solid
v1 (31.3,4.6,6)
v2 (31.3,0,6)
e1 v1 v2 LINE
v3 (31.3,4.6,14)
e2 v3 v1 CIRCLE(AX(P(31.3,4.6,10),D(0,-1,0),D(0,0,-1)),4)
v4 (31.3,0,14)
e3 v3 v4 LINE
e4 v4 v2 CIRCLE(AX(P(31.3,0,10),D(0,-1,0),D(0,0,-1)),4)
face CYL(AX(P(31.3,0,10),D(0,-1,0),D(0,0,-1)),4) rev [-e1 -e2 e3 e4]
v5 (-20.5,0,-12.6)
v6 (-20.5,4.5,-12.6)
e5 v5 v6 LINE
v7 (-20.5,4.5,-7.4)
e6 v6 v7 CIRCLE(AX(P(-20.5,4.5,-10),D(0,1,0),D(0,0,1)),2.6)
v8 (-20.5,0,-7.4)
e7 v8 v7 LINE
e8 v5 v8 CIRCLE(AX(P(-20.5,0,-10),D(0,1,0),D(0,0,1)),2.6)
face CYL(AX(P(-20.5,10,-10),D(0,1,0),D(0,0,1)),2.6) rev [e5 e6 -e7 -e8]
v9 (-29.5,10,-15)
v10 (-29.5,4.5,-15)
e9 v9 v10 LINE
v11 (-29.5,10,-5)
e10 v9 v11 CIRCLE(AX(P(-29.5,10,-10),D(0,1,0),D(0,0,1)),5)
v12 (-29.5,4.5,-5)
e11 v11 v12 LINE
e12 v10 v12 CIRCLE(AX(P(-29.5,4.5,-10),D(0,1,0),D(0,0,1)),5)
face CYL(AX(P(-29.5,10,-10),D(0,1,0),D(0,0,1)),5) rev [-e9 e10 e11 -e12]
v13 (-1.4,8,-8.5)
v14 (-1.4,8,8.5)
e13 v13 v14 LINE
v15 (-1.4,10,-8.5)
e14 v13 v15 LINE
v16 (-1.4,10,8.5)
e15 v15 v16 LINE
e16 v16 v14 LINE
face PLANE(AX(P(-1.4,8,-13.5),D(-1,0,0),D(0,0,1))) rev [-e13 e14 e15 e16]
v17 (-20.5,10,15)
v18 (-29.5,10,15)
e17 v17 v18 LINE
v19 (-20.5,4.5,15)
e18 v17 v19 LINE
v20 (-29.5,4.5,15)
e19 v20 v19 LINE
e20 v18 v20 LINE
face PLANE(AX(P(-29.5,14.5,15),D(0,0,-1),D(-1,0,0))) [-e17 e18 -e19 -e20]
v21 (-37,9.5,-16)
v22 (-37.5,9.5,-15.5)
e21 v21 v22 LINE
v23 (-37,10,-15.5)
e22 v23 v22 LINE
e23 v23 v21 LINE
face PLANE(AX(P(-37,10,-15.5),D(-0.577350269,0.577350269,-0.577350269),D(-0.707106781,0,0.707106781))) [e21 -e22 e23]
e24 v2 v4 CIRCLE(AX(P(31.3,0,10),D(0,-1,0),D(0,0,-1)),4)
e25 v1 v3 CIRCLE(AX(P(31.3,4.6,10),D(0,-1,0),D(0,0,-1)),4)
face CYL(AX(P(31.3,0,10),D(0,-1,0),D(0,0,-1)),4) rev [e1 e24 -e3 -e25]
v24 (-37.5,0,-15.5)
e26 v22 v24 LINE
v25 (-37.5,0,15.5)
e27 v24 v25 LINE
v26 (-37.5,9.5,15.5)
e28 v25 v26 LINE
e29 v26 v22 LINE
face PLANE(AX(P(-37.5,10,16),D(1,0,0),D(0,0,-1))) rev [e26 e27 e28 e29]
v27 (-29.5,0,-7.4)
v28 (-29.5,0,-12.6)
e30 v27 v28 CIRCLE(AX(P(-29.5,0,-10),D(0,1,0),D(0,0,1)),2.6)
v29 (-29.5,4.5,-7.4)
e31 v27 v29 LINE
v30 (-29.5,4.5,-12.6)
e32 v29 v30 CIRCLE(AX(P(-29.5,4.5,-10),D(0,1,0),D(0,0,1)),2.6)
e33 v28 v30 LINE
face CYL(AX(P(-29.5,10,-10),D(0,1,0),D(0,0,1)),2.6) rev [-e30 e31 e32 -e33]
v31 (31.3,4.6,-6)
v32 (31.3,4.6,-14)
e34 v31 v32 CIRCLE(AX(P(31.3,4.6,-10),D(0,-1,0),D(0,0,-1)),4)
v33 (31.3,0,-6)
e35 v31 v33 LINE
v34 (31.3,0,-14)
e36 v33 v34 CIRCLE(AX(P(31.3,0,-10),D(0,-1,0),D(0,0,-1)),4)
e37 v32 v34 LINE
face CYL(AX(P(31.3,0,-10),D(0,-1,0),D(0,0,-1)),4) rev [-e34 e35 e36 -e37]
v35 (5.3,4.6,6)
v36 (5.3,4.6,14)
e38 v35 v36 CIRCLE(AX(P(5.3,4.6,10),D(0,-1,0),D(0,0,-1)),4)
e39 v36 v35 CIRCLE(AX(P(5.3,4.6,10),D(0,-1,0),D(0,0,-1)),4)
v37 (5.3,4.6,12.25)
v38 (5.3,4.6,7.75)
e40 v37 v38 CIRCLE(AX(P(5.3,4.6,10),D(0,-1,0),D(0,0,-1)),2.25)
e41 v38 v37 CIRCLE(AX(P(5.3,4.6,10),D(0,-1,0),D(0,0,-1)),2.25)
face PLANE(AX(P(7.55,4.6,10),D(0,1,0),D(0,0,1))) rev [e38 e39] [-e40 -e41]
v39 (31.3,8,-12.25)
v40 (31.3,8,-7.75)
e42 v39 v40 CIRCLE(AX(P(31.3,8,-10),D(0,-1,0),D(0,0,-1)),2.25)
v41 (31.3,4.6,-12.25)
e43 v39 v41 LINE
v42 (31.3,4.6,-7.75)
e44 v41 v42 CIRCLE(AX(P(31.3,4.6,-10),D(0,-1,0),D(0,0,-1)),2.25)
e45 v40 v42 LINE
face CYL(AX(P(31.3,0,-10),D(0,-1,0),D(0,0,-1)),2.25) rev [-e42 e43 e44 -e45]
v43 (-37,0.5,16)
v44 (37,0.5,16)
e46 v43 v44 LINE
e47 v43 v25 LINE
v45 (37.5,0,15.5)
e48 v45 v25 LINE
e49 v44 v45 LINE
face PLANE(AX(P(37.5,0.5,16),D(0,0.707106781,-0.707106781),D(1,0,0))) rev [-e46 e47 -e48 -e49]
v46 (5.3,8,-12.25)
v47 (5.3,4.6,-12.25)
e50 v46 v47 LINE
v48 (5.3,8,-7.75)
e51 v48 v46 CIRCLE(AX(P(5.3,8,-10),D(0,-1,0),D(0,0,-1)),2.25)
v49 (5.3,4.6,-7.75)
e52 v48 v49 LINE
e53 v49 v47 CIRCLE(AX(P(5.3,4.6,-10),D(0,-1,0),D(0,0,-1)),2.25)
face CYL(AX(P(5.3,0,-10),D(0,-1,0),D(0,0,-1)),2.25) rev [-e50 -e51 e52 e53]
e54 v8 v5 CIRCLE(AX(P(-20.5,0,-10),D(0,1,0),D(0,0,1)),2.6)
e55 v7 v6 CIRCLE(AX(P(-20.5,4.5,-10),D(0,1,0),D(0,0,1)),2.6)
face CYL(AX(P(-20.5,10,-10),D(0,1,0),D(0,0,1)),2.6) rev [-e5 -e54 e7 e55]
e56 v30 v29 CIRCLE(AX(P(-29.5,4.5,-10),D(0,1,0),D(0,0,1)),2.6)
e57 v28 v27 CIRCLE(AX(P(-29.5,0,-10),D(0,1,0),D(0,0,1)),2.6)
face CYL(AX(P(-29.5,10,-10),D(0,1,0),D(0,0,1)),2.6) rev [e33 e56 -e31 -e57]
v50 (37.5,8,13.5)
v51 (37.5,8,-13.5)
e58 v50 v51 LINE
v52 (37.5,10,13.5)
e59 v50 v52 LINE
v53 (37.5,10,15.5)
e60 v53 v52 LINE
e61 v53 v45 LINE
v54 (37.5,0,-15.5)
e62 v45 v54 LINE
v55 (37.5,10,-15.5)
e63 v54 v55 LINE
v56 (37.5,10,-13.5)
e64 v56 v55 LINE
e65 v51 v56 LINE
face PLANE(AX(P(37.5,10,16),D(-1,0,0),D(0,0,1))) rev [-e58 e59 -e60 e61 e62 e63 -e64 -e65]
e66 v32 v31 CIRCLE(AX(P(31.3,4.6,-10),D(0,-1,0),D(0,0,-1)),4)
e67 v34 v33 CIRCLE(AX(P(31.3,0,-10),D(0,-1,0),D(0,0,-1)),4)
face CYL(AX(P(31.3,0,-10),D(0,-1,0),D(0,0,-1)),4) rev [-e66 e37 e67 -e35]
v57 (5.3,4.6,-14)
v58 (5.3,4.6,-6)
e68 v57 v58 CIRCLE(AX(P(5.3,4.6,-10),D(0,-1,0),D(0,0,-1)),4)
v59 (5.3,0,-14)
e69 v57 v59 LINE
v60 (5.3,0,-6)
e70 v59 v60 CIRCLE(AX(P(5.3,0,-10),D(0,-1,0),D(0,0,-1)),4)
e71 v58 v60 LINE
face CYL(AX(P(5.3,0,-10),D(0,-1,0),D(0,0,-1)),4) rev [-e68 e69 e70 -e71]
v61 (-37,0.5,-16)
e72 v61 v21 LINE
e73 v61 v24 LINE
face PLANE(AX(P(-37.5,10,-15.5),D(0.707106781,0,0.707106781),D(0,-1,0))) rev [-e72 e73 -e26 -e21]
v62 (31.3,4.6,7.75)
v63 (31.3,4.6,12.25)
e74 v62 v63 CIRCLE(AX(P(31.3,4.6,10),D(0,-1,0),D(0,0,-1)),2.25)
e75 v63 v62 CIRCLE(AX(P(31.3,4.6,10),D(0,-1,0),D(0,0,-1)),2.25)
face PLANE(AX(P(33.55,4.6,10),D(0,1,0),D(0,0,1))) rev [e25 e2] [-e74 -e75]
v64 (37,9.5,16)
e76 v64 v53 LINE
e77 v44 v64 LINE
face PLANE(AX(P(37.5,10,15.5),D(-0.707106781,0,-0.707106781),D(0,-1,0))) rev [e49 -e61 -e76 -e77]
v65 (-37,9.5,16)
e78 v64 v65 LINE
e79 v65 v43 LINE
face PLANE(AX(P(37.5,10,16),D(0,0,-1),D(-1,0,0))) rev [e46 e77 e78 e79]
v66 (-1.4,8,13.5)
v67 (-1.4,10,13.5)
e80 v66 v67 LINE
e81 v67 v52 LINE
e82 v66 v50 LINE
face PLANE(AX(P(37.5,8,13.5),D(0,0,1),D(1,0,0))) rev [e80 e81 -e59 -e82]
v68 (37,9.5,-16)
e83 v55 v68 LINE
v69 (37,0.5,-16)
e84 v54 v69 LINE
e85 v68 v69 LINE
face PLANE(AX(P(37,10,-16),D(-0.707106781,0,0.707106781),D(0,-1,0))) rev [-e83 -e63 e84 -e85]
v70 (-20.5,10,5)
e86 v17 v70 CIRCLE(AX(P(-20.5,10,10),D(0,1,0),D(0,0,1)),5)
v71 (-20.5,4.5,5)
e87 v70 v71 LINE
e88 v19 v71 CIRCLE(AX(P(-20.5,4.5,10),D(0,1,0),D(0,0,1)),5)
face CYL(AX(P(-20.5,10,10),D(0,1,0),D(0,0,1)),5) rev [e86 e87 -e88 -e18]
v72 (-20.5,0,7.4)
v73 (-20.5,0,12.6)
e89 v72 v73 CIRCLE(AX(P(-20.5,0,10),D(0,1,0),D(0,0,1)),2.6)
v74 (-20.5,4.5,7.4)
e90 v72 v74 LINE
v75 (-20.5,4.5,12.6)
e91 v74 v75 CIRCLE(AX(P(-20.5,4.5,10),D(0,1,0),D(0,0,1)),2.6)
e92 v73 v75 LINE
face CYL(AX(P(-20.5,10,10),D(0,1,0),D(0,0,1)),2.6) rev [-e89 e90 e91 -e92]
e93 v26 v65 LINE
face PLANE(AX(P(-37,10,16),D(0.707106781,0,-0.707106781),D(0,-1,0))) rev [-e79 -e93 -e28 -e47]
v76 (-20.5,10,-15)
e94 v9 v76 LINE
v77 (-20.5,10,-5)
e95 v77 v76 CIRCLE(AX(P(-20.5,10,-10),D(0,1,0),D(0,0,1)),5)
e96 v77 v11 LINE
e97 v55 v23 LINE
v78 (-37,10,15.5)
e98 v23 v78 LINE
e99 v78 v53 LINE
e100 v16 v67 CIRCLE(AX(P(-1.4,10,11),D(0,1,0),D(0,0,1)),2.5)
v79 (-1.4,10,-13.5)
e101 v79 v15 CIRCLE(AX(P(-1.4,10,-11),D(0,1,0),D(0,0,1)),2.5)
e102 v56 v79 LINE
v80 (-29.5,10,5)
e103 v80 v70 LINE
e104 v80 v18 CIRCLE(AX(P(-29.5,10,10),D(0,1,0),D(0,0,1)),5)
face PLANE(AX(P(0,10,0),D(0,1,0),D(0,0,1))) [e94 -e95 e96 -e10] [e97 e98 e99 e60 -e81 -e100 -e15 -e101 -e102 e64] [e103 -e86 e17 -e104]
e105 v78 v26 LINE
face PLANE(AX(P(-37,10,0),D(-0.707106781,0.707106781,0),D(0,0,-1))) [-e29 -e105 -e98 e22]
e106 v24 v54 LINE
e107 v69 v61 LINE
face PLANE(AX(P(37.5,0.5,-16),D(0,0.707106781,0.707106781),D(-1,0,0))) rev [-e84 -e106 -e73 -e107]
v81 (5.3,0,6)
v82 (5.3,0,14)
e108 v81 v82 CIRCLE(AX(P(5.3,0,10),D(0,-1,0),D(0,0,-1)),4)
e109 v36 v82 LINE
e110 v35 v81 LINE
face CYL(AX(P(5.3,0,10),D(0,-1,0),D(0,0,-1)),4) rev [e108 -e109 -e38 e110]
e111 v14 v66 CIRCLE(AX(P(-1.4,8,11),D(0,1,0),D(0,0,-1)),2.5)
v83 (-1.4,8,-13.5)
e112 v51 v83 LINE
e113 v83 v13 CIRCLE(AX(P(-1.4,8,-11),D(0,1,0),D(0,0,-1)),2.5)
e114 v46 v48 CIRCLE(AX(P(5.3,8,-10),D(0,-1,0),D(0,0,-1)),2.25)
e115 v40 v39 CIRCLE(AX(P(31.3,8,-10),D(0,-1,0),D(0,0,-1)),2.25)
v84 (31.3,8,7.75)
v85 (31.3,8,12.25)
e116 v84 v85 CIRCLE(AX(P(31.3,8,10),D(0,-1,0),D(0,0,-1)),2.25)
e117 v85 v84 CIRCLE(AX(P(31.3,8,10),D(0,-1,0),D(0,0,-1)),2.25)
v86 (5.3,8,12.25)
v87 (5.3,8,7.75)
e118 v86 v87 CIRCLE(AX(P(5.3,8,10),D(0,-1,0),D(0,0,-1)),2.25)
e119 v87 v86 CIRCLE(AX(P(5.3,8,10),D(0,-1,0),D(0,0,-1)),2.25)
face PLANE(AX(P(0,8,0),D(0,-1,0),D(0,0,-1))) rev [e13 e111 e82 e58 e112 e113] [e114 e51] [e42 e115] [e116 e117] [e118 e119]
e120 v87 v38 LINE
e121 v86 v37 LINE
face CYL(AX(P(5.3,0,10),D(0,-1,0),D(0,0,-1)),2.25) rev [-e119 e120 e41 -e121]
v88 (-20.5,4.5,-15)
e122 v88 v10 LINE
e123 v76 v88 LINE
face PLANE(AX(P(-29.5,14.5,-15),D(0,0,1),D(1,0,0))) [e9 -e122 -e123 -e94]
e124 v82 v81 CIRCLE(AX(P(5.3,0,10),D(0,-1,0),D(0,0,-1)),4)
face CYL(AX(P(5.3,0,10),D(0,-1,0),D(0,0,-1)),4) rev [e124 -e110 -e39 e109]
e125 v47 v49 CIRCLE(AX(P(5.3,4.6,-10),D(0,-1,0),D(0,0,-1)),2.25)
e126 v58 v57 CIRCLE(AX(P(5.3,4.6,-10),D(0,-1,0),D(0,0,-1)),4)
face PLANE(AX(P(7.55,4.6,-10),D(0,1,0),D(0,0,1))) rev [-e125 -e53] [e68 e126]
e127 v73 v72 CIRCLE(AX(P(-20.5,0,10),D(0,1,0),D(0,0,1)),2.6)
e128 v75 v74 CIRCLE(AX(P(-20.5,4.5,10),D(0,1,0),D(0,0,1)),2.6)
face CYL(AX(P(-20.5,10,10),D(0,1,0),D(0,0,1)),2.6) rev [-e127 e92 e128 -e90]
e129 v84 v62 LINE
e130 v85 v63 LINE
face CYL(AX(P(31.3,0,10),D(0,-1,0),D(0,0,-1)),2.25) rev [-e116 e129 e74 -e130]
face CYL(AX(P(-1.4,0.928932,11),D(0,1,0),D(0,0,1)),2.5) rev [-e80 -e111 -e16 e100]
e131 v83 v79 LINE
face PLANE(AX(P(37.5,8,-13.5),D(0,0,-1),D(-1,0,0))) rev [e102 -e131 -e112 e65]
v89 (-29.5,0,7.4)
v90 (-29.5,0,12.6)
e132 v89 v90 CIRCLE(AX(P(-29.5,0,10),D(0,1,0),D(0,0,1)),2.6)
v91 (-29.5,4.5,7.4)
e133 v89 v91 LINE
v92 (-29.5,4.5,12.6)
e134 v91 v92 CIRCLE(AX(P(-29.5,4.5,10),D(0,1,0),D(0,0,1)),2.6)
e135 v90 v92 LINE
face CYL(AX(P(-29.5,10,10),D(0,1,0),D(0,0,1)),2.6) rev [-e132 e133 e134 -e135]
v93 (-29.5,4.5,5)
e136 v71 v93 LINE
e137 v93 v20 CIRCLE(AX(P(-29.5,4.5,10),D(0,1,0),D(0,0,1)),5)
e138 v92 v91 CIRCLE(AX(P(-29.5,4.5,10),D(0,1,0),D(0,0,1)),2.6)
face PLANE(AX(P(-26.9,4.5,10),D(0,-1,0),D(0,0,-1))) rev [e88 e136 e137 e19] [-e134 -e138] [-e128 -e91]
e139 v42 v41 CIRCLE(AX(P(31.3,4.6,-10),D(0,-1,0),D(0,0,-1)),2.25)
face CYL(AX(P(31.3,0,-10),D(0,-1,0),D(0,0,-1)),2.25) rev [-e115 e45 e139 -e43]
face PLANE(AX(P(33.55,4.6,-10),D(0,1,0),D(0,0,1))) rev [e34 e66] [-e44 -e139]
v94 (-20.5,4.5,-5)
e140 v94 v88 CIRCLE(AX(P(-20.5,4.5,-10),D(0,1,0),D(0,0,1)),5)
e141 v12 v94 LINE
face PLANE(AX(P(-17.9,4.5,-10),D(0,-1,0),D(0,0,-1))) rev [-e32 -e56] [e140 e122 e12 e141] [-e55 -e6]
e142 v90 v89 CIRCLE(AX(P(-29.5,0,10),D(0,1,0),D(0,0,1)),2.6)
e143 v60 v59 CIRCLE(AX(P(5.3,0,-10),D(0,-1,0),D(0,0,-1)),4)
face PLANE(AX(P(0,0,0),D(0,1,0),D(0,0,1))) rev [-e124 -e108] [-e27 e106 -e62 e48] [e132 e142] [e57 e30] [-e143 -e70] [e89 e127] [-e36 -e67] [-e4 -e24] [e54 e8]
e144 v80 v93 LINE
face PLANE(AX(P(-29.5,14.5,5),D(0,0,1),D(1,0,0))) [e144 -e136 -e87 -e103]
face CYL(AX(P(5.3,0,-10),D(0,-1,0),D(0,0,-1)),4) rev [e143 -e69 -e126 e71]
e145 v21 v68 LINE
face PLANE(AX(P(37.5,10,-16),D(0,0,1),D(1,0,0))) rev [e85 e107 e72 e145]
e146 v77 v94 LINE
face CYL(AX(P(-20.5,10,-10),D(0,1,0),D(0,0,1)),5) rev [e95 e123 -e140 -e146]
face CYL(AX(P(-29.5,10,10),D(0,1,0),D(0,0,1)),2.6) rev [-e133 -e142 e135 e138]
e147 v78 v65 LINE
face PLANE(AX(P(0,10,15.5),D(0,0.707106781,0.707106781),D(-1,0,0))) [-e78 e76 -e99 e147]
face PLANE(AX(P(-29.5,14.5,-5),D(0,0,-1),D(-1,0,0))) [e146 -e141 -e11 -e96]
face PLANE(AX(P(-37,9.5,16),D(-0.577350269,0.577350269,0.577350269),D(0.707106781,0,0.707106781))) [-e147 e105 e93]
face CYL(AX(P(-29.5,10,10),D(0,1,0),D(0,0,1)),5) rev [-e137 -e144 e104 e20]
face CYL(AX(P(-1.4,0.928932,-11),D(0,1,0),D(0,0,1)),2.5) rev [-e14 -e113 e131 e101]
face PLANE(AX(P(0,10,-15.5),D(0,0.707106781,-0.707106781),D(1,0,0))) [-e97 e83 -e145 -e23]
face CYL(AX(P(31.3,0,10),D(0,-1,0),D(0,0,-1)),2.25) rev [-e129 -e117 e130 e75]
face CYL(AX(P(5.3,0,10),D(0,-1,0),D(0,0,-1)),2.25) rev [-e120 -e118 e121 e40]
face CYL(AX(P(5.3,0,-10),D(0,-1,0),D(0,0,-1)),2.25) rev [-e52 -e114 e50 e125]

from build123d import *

# Parameters (mm, degrees)
SKETCH1_W                                            = 75
SKETCH1_H                                            = 32
EXTRUDE1_DEPTH                                       = 10
SKETCH2_W                                            = 38.9
SKETCH2_H                                            = 27
EXTRUDE2_DEPTH                                       = 2
CBORE_FOR_M4_HEXAGON_SOCKET_HEAD_CAP_SCR_D           = 4.5
CBORE_FOR_M4_HEXAGON_SOCKET_HEAD_CAP_SCR_CBORE_D     = 8
CBORE_FOR_M4_HEXAGON_SOCKET_HEAD_CAP_SCR_CBORE_DEPTH = 4.6
CBORE_FOR_M5_HEXAGON_SOCKET_HEAD_CAP_SCR_D           = 5.2
CBORE_FOR_M5_HEXAGON_SOCKET_HEAD_CAP_SCR_CBORE_D     = 10
CBORE_FOR_M5_HEXAGON_SOCKET_HEAD_CAP_SCR_CBORE_DEPTH = 5.5
EXTRUDE4_START                                       = 10
EXTRUDE4_DEPTH                                       = 10
SKETCH11_R                                           = 2.5
EXTRUDE6_DEPTH                                       = 2
CHAMFER1_SIZE                                        = 0.5


with BuildPart() as part:
    # Sketch1 → Extrude1 (new body)
    with BuildSketch(Plane(origin=(0, 0, 0), x_dir=(1, 0, 0), z_dir=(0, 1, 0))):
        Rectangle(SKETCH1_W, SKETCH1_H)
    extrude(amount=EXTRUDE1_DEPTH)

    # Sketch2 → Extrude2 (cut)
    with BuildSketch(Plane(origin=(0, 10, 0), x_dir=(1, 0, 0), z_dir=(0, 1, 0))):
        with Locations((18.05, 0)):
            Rectangle(SKETCH2_W, SKETCH2_H)
    extrude(amount=-EXTRUDE2_DEPTH, mode=Mode.SUBTRACT)

    # CBORE for M4 Hexagon socket head cap screws1 (through all)
    with Locations(Plane(origin=(0, 0, 0), x_dir=(-1, 0, 0), z_dir=(0, -1, 0))):
        with Locations((-31.3, -10), (-31.3, 10), (-5.3, 10), (-5.3, -10)):
            CounterBoreHole(CBORE_FOR_M4_HEXAGON_SOCKET_HEAD_CAP_SCR_D / 2, CBORE_FOR_M4_HEXAGON_SOCKET_HEAD_CAP_SCR_CBORE_D / 2, CBORE_FOR_M4_HEXAGON_SOCKET_HEAD_CAP_SCR_CBORE_DEPTH)

    # CBORE for M5 Hexagon socket head cap screws1 (through all)
    with Locations(Plane(origin=(0, 10, 0), x_dir=(1, 0, 0), z_dir=(0, 1, 0))):
        with Locations((-29.5, 10), (-20.5, 10), (-20.5, -10), (-29.5, -10)):
            CounterBoreHole(CBORE_FOR_M5_HEXAGON_SOCKET_HEAD_CAP_SCR_D / 2, CBORE_FOR_M5_HEXAGON_SOCKET_HEAD_CAP_SCR_CBORE_D / 2, CBORE_FOR_M5_HEXAGON_SOCKET_HEAD_CAP_SCR_CBORE_DEPTH)

    # Sketch10 → Extrude4 (cut)
    with BuildSketch(Plane(origin=(0, 4.5, 0), x_dir=(1, 0, 0), z_dir=(0, 1, 0)).offset(EXTRUDE4_START)):
        with BuildLine():
            Line((-29.5, 15), (-20.5, 15))
            ThreePointArc((-20.5, 15), (-15.5, 10), (-20.5, 5))
            Line((-20.5, 5), (-29.5, 5))
            ThreePointArc((-29.5, 5), (-34.5, 10), (-29.5, 15))
        make_face()
        with BuildLine():
            Line((-29.5, -5), (-20.5, -5))
            ThreePointArc((-20.5, -5), (-15.5, -10), (-20.5, -15))
            Line((-20.5, -15), (-29.5, -15))
            ThreePointArc((-29.5, -15), (-34.5, -10), (-29.5, -5))
        make_face()
    extrude(amount=-EXTRUDE4_DEPTH, mode=Mode.SUBTRACT)

    # Sketch11 → Extrude6 (cut)
    with BuildSketch(Plane(origin=(0, 10, 0), x_dir=(1, 0, 0), z_dir=(0, 1, 0))):
        with Locations((-1.4, 11)):
            Circle(SKETCH11_R)
        with Locations((-1.4, -11)):
            Circle(SKETCH11_R)
    extrude(amount=-EXTRUDE6_DEPTH, mode=Mode.SUBTRACT)

    # Chamfer1
    chamfer1_edges = [part.edges().sort_by_distance(p)[0] for p in [
        (0, 10, -16),
        (-37.5, 10, 0),
        (0, 0, -16),
        (0, 0, 16),
        (0, 10, 16),
        (-37.5, 5, -16),
        (37.5, 5, -16),
        (37.5, 5, 16),
        (-37.5, 5, 16),
    ]]
    chamfer(chamfer1_edges, length=CHAMFER1_SIZE)


solid = part.part
